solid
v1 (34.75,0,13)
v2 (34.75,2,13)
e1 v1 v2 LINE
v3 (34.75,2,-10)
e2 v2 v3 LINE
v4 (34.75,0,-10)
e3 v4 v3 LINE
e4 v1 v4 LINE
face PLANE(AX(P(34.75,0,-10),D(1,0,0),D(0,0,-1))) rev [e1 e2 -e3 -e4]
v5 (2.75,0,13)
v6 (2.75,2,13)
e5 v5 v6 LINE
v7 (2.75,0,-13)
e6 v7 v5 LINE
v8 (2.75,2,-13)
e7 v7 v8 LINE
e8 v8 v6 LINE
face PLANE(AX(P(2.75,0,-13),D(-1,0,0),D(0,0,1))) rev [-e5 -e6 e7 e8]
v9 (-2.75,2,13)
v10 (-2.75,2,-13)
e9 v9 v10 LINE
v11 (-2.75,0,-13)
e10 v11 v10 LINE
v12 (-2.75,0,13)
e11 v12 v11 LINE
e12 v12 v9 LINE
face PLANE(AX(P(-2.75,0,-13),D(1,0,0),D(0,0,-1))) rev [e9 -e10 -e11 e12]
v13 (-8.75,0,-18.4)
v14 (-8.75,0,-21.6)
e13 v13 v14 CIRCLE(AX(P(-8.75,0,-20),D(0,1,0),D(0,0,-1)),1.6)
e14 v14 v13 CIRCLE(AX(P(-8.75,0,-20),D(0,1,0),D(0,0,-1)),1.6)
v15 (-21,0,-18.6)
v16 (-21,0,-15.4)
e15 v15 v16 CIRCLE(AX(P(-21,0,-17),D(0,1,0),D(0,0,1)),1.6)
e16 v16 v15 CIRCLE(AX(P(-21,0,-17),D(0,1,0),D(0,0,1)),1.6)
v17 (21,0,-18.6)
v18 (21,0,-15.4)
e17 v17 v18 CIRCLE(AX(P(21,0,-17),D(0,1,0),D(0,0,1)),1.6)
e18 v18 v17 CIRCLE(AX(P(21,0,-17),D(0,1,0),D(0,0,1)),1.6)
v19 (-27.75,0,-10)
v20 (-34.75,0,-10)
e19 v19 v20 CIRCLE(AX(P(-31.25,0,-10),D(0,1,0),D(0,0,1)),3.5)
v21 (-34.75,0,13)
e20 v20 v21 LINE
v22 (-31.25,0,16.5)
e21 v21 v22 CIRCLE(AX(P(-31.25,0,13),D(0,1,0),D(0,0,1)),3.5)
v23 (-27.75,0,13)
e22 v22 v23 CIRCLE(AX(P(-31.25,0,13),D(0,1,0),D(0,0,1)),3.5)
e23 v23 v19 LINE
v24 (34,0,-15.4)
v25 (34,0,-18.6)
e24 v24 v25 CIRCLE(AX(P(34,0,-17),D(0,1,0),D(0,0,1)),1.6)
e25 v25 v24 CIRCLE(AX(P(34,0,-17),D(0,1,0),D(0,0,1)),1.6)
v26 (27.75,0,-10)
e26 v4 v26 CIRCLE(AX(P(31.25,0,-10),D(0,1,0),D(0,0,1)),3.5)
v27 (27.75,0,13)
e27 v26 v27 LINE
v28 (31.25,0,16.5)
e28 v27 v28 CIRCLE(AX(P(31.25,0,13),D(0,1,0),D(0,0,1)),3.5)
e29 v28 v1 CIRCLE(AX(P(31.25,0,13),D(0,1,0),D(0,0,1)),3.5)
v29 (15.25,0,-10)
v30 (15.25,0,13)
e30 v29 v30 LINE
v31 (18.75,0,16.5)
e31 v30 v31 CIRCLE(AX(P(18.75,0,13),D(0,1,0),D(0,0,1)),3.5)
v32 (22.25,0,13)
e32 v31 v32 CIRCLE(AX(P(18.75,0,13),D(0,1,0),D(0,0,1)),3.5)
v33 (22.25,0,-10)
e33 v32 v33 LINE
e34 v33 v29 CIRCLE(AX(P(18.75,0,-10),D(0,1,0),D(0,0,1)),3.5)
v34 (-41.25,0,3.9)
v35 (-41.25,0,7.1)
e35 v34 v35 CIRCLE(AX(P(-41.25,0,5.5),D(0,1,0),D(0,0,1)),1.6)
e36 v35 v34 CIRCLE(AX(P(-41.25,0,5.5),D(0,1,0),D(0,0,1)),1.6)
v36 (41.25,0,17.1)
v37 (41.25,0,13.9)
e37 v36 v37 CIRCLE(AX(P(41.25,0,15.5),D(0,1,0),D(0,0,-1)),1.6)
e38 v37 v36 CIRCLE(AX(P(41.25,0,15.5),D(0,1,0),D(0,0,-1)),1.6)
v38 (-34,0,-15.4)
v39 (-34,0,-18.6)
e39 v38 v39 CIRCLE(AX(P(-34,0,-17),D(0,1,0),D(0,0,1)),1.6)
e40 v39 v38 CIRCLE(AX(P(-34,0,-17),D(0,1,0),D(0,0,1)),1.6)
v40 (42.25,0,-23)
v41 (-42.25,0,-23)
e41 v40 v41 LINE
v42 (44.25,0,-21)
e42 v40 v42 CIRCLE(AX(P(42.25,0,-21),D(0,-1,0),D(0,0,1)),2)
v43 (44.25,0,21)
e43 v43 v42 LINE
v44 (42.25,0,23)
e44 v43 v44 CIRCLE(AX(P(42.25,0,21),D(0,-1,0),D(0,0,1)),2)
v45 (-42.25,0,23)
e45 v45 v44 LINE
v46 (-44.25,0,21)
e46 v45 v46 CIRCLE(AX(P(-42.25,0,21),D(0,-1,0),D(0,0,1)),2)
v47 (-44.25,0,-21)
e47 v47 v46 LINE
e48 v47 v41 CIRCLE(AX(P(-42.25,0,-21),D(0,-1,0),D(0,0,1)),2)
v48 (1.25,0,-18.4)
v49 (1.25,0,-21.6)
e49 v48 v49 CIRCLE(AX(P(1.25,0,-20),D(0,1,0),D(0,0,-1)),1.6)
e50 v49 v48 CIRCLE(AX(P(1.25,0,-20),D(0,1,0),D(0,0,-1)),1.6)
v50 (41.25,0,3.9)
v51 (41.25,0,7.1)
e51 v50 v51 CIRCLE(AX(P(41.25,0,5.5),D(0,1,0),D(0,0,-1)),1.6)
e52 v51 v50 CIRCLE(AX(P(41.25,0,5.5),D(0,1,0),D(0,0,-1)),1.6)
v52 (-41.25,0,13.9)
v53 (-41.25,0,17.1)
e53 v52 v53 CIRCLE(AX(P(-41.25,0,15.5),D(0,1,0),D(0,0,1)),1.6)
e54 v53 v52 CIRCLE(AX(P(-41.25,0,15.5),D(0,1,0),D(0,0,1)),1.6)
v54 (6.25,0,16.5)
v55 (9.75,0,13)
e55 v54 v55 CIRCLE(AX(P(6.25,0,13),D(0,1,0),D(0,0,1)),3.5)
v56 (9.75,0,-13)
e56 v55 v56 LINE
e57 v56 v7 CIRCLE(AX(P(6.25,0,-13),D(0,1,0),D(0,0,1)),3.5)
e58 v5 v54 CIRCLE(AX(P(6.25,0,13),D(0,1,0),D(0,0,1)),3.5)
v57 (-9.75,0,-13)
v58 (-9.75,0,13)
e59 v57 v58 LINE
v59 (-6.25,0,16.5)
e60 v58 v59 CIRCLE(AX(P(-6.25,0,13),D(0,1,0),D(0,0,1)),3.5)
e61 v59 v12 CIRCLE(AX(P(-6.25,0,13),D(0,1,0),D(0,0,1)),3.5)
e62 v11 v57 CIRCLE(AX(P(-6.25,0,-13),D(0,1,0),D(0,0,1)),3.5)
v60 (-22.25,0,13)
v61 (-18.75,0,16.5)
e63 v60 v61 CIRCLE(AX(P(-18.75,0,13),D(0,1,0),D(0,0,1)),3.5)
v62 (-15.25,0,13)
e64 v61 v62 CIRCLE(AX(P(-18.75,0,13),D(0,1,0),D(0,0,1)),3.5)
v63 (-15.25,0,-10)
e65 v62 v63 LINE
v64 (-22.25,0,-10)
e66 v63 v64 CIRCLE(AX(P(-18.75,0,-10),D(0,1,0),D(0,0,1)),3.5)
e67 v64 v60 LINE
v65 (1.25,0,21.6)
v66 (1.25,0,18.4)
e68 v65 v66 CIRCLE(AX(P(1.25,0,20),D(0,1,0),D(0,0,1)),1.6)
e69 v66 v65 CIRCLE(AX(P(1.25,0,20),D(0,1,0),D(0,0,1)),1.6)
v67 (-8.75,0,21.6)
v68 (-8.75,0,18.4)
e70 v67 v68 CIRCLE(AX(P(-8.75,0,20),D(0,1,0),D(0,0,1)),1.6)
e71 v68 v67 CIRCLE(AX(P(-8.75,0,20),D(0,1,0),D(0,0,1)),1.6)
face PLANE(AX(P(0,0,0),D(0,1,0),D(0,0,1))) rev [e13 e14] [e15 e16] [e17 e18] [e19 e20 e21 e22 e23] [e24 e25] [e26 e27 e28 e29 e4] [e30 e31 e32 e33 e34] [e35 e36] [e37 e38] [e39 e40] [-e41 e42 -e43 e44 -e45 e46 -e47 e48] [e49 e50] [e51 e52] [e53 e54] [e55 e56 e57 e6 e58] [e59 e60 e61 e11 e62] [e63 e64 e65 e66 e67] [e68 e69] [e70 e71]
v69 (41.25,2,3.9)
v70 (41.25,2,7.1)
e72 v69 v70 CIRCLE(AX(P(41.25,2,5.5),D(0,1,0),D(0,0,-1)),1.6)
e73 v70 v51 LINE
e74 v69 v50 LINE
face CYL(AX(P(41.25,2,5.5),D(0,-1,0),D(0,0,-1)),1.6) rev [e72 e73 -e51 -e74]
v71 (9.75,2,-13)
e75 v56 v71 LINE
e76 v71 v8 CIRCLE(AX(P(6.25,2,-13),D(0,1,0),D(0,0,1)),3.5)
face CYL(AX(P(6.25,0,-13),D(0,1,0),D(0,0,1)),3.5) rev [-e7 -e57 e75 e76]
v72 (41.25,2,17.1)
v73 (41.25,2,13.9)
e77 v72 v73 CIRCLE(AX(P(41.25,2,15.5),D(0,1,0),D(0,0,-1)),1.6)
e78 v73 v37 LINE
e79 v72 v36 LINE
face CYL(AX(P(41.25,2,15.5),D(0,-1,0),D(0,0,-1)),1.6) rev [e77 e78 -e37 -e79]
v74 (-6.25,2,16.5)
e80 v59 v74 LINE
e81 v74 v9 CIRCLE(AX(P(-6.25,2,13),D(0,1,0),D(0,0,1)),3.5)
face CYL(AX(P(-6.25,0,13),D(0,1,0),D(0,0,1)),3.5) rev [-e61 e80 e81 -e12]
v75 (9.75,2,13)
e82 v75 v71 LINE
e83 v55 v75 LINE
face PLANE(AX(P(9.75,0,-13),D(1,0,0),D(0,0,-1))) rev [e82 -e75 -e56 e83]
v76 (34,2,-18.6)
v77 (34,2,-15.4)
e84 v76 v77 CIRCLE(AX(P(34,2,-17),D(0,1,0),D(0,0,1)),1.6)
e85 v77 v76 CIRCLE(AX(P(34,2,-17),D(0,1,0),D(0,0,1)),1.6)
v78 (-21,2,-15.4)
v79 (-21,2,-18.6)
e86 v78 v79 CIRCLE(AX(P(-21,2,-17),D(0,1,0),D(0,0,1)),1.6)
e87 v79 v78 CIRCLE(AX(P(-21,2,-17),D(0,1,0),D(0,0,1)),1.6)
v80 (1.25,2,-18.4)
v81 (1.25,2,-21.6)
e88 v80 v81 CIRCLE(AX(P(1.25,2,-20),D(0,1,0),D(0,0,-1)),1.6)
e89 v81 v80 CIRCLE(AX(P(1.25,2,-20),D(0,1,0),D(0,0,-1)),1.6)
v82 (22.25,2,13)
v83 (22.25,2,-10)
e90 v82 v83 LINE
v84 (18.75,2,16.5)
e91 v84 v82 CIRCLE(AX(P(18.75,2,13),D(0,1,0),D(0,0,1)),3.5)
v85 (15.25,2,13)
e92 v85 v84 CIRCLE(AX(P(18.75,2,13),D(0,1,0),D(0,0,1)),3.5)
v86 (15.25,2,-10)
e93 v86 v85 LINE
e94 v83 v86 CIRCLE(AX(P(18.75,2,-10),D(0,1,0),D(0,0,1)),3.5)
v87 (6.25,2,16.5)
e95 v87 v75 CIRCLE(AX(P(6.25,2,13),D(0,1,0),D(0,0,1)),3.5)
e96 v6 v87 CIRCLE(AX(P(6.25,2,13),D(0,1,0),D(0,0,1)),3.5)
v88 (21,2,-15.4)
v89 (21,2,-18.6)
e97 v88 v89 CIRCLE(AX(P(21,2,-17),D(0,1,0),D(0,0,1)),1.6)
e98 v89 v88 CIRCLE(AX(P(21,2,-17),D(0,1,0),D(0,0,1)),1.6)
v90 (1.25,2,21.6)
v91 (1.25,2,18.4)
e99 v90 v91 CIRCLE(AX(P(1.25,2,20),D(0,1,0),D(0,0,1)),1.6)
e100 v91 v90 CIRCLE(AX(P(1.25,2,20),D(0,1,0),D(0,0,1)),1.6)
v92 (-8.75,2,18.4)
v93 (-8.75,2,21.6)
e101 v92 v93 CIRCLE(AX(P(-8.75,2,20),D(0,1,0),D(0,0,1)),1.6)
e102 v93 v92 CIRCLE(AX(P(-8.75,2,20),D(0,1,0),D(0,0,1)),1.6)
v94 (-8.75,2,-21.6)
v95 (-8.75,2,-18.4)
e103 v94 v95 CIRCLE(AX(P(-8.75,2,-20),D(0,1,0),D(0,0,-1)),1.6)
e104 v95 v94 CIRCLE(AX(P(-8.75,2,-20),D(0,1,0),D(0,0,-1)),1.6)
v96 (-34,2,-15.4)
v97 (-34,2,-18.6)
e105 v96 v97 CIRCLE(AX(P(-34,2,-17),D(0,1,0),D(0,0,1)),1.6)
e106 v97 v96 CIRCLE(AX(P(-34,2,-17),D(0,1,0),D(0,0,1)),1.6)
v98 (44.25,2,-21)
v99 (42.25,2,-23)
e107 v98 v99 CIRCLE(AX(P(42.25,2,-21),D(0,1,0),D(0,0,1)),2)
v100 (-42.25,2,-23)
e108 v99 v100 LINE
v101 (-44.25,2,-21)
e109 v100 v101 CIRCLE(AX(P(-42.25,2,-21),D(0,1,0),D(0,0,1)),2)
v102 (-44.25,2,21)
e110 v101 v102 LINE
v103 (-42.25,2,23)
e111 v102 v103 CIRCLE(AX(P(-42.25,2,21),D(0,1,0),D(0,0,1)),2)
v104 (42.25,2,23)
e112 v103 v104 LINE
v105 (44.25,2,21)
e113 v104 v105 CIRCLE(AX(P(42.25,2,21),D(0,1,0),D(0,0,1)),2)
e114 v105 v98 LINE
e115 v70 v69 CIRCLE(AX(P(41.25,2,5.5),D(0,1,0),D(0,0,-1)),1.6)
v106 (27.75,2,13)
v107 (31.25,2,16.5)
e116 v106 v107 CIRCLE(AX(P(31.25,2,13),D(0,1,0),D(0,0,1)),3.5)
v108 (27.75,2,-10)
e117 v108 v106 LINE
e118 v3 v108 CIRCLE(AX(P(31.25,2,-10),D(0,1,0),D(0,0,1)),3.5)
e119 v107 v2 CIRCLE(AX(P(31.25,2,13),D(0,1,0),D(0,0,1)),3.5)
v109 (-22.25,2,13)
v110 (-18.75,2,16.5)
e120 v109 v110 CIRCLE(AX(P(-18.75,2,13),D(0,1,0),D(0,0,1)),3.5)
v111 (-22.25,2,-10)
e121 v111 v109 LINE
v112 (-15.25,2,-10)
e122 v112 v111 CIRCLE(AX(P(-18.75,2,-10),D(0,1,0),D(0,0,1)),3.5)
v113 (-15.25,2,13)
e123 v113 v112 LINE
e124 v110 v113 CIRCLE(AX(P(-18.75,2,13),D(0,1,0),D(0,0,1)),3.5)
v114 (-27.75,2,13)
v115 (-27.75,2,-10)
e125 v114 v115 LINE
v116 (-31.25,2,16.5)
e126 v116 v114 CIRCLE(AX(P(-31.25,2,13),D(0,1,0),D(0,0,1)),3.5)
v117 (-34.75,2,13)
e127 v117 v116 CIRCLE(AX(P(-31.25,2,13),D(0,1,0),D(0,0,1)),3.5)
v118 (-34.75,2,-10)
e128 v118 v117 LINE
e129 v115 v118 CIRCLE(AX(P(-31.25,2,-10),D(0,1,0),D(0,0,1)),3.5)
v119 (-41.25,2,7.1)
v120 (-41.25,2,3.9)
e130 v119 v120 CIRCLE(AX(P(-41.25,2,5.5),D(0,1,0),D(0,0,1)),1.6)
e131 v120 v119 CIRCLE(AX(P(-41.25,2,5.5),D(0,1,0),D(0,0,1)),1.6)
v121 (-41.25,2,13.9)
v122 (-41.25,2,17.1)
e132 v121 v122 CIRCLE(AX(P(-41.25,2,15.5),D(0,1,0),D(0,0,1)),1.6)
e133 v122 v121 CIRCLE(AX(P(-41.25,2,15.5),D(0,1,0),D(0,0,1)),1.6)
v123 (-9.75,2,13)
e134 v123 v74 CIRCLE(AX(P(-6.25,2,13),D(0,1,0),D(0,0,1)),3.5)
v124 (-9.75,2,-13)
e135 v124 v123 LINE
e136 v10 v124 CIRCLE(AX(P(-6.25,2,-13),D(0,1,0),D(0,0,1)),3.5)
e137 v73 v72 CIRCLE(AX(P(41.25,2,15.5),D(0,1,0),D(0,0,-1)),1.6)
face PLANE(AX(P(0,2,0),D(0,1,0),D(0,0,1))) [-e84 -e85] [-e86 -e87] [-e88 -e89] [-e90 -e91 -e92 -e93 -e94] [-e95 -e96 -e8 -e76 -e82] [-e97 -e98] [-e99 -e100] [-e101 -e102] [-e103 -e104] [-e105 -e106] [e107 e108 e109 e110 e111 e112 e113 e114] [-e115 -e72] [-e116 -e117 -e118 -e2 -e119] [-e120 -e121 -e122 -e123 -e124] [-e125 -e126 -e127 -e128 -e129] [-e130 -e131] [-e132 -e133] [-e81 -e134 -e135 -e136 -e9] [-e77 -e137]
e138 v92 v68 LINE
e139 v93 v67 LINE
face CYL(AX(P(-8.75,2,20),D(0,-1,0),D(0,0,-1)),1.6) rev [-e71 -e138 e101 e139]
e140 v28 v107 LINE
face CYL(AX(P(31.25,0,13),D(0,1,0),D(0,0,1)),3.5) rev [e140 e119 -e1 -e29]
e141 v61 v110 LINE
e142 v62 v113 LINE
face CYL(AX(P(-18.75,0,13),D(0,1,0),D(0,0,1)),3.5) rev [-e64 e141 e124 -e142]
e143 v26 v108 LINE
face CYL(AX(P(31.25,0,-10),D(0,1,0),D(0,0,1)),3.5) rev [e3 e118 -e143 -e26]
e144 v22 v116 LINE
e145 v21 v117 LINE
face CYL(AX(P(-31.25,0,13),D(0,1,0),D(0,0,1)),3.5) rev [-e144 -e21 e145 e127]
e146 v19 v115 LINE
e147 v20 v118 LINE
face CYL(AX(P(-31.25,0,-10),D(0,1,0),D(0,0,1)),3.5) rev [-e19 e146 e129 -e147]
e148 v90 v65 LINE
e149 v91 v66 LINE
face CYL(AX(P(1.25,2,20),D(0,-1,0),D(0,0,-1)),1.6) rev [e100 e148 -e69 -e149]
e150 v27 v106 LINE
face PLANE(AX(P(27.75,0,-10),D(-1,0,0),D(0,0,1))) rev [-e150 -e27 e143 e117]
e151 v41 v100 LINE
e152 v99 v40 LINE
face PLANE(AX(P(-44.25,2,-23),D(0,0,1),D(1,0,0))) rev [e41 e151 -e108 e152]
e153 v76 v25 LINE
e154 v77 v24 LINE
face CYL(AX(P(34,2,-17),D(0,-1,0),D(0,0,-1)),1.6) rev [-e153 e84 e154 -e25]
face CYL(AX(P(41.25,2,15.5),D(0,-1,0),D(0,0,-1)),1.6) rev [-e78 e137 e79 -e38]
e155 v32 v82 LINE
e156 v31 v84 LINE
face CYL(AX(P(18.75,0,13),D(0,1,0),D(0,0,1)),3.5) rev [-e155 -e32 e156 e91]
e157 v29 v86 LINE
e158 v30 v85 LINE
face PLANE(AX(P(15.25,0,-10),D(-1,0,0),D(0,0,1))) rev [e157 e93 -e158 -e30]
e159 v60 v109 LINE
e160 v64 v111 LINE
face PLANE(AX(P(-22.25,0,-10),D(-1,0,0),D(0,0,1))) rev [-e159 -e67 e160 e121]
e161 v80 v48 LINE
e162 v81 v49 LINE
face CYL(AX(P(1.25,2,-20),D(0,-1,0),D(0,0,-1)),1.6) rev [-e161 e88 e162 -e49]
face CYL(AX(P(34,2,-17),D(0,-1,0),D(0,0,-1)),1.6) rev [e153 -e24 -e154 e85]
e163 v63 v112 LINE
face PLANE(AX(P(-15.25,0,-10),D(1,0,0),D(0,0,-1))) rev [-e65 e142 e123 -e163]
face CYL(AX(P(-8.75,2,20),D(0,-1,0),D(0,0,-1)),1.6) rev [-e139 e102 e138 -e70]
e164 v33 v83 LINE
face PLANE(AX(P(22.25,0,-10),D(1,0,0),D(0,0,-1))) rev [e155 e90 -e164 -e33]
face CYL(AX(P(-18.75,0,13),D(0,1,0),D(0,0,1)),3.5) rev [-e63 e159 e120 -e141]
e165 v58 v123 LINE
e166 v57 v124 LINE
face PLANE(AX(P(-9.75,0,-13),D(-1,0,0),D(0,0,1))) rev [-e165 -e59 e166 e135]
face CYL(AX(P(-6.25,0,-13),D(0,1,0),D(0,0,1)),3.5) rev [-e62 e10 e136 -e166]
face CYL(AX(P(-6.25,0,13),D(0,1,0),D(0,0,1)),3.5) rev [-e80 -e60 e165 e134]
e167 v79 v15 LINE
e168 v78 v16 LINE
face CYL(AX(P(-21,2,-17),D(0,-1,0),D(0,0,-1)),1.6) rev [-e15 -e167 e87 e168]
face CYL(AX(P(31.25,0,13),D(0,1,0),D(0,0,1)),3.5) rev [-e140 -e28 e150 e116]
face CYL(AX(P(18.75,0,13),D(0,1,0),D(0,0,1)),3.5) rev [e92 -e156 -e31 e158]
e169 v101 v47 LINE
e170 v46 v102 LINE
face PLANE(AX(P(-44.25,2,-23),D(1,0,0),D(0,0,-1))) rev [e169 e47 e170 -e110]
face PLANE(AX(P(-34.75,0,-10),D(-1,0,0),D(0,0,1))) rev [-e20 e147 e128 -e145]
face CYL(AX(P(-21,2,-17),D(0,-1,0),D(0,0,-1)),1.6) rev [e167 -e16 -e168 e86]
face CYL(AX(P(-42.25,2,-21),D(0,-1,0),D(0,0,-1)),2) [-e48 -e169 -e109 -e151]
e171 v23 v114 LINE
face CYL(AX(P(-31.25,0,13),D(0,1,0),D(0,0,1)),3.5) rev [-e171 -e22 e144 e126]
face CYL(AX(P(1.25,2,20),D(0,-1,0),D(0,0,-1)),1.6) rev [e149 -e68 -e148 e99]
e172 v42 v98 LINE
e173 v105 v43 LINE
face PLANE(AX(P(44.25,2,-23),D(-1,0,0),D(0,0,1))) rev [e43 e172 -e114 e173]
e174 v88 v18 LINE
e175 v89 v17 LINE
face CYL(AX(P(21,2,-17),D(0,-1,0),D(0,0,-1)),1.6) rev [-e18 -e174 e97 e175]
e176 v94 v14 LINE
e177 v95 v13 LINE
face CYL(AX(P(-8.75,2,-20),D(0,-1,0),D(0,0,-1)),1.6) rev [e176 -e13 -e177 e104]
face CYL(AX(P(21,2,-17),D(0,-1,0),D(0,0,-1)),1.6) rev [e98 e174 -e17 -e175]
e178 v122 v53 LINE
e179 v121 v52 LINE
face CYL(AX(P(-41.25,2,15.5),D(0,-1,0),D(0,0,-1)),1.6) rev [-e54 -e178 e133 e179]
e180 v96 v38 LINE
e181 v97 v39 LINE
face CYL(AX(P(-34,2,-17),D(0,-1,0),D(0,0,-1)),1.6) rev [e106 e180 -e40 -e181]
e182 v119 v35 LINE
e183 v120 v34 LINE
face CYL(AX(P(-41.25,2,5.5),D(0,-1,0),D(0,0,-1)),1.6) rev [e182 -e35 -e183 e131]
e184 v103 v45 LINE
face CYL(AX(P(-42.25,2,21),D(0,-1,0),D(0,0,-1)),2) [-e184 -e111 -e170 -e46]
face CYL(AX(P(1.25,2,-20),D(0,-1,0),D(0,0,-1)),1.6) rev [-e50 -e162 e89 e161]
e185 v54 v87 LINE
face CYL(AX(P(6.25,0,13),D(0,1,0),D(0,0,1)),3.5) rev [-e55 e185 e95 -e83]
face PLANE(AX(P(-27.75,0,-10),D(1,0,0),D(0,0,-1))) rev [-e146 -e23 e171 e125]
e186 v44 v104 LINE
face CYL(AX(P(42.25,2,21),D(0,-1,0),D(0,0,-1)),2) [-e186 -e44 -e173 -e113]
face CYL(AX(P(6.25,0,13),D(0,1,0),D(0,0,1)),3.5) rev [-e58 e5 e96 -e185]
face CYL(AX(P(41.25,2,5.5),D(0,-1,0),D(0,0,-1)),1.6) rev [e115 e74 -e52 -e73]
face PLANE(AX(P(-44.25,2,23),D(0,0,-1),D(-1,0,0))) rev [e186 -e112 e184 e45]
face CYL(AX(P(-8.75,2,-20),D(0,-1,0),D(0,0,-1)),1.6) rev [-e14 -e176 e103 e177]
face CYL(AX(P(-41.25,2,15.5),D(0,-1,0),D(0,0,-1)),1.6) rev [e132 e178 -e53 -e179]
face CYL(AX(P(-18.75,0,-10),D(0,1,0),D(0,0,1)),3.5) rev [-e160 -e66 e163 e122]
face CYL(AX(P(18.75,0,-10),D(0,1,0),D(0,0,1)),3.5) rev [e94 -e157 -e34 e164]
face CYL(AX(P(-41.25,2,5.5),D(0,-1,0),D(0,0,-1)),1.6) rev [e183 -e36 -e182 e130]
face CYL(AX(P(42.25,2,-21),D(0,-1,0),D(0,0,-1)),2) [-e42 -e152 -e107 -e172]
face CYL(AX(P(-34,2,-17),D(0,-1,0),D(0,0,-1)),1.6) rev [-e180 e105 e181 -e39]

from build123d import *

# Parameters (mm, degrees)
SKETCH1_W           = 88.5
SKETCH1_H           = 46
SKETCH1_R           = 1.6
BOSS_EXTRUDE1_DEPTH = 2
CUT_EXTRUDE1_DEPTH  = 50.910544978
FILLET1_R           = 2


with BuildPart() as part:
    # Sketch1 → Boss-Extrude1 (new body)
    with BuildSketch(Plane(origin=(0, 0, 0), x_dir=(1, 0, 0), z_dir=(0, 1, 0))):
        Rectangle(SKETCH1_W, SKETCH1_H)
        with Locations(Location((-41.25, -5.5, 0), (0, 0, 270))):
            Circle(SKETCH1_R, mode=Mode.SUBTRACT)
        with Locations(Location((-41.25, -15.5, 0), (0, 0, 270))):
            Circle(SKETCH1_R, mode=Mode.SUBTRACT)
        with Locations(Location((41.25, -15.5, 0), (0, 0, 90))):
            Circle(SKETCH1_R, mode=Mode.SUBTRACT)
        with Locations(Location((41.25, -5.5, 0), (0, 0, 90))):
            Circle(SKETCH1_R, mode=Mode.SUBTRACT)
        with Locations(Location((-8.75, -20, 0), (0, 0, 270))):
            Circle(SKETCH1_R, mode=Mode.SUBTRACT)
        with Locations(Location((1.25, -20, 0), (0, 0, 270))):
            Circle(SKETCH1_R, mode=Mode.SUBTRACT)
        with Locations(Location((-34, 17, 0), (0, 0, 270))):
            Circle(SKETCH1_R, mode=Mode.SUBTRACT)
        with Locations(Location((-21, 17, 0), (0, 0, 270))):
            Circle(SKETCH1_R, mode=Mode.SUBTRACT)
        with Locations(Location((21, 17, 0), (0, 0, 270))):
            Circle(SKETCH1_R, mode=Mode.SUBTRACT)
        with Locations(Location((34, 17, 0), (0, 0, 270))):
            Circle(SKETCH1_R, mode=Mode.SUBTRACT)
        with Locations(Location((1.25, 20, 0), (0, 0, 90))):
            Circle(SKETCH1_R, mode=Mode.SUBTRACT)
        with Locations(Location((-8.75, 20, 0), (0, 0, 90))):
            Circle(SKETCH1_R, mode=Mode.SUBTRACT)
    extrude(amount=BOSS_EXTRUDE1_DEPTH)

    # Sketch2 → Cut-Extrude1 (cut, through all)
    with BuildSketch(Plane(origin=(0, 2, 0), x_dir=(1, 0, 0), z_dir=(0, 1, 0))):
        with BuildLine():
            Line((-27.75, 10), (-27.75, -13))
            ThreePointArc((-27.75, -13), (-31.25, -16.5), (-34.75, -13))
            Line((-34.75, -13), (-34.75, 10))
            ThreePointArc((-34.75, 10), (-31.25, 13.5), (-27.75, 10))
        make_face()
        with BuildLine():
            Line((-15.25, 10), (-15.25, -13))
            ThreePointArc((-15.25, -13), (-18.75, -16.5), (-22.25, -13))
            Line((-22.25, -13), (-22.25, 10))
            ThreePointArc((-22.25, 10), (-18.75, 13.5), (-15.25, 10))
        make_face()
        with BuildLine():
            Line((-2.75, 13), (-2.75, -13))
            ThreePointArc((-2.75, -13), (-6.25, -16.5), (-9.75, -13))
            Line((-9.75, -13), (-9.75, 13))
            ThreePointArc((-9.75, 13), (-6.25, 16.5), (-2.75, 13))
        make_face()
        with BuildLine():
            Line((9.75, 13), (9.75, -13))
            ThreePointArc((9.75, -13), (6.25, -16.5), (2.75, -13))
            Line((2.75, -13), (2.75, 13))
            ThreePointArc((2.75, 13), (6.25, 16.5), (9.75, 13))
        make_face()
        with BuildLine():
            Line((22.25, 10), (22.25, -13))
            ThreePointArc((22.25, -13), (18.75, -16.5), (15.25, -13))
            Line((15.25, -13), (15.25, 10))
            ThreePointArc((15.25, 10), (18.75, 13.5), (22.25, 10))
        make_face()
        with BuildLine():
            Line((34.75, 10), (34.75, -13))
            ThreePointArc((34.75, -13), (31.25, -16.5), (27.75, -13))
            Line((27.75, -13), (27.75, 10))
            ThreePointArc((27.75, 10), (31.25, 13.5), (34.75, 10))
        make_face()
    extrude(amount=-CUT_EXTRUDE1_DEPTH, mode=Mode.SUBTRACT)

    # Fillet1
    fillet1_edges = [part.edges().sort_by_distance(p)[0] for p in [
        (44.25, 1, 23),
        (-44.25, 1, 23),
        (-44.25, 1, -23),
        (44.25, 1, -23),
    ]]
    fillet(fillet1_edges, radius=FILLET1_R)


solid = part.part
